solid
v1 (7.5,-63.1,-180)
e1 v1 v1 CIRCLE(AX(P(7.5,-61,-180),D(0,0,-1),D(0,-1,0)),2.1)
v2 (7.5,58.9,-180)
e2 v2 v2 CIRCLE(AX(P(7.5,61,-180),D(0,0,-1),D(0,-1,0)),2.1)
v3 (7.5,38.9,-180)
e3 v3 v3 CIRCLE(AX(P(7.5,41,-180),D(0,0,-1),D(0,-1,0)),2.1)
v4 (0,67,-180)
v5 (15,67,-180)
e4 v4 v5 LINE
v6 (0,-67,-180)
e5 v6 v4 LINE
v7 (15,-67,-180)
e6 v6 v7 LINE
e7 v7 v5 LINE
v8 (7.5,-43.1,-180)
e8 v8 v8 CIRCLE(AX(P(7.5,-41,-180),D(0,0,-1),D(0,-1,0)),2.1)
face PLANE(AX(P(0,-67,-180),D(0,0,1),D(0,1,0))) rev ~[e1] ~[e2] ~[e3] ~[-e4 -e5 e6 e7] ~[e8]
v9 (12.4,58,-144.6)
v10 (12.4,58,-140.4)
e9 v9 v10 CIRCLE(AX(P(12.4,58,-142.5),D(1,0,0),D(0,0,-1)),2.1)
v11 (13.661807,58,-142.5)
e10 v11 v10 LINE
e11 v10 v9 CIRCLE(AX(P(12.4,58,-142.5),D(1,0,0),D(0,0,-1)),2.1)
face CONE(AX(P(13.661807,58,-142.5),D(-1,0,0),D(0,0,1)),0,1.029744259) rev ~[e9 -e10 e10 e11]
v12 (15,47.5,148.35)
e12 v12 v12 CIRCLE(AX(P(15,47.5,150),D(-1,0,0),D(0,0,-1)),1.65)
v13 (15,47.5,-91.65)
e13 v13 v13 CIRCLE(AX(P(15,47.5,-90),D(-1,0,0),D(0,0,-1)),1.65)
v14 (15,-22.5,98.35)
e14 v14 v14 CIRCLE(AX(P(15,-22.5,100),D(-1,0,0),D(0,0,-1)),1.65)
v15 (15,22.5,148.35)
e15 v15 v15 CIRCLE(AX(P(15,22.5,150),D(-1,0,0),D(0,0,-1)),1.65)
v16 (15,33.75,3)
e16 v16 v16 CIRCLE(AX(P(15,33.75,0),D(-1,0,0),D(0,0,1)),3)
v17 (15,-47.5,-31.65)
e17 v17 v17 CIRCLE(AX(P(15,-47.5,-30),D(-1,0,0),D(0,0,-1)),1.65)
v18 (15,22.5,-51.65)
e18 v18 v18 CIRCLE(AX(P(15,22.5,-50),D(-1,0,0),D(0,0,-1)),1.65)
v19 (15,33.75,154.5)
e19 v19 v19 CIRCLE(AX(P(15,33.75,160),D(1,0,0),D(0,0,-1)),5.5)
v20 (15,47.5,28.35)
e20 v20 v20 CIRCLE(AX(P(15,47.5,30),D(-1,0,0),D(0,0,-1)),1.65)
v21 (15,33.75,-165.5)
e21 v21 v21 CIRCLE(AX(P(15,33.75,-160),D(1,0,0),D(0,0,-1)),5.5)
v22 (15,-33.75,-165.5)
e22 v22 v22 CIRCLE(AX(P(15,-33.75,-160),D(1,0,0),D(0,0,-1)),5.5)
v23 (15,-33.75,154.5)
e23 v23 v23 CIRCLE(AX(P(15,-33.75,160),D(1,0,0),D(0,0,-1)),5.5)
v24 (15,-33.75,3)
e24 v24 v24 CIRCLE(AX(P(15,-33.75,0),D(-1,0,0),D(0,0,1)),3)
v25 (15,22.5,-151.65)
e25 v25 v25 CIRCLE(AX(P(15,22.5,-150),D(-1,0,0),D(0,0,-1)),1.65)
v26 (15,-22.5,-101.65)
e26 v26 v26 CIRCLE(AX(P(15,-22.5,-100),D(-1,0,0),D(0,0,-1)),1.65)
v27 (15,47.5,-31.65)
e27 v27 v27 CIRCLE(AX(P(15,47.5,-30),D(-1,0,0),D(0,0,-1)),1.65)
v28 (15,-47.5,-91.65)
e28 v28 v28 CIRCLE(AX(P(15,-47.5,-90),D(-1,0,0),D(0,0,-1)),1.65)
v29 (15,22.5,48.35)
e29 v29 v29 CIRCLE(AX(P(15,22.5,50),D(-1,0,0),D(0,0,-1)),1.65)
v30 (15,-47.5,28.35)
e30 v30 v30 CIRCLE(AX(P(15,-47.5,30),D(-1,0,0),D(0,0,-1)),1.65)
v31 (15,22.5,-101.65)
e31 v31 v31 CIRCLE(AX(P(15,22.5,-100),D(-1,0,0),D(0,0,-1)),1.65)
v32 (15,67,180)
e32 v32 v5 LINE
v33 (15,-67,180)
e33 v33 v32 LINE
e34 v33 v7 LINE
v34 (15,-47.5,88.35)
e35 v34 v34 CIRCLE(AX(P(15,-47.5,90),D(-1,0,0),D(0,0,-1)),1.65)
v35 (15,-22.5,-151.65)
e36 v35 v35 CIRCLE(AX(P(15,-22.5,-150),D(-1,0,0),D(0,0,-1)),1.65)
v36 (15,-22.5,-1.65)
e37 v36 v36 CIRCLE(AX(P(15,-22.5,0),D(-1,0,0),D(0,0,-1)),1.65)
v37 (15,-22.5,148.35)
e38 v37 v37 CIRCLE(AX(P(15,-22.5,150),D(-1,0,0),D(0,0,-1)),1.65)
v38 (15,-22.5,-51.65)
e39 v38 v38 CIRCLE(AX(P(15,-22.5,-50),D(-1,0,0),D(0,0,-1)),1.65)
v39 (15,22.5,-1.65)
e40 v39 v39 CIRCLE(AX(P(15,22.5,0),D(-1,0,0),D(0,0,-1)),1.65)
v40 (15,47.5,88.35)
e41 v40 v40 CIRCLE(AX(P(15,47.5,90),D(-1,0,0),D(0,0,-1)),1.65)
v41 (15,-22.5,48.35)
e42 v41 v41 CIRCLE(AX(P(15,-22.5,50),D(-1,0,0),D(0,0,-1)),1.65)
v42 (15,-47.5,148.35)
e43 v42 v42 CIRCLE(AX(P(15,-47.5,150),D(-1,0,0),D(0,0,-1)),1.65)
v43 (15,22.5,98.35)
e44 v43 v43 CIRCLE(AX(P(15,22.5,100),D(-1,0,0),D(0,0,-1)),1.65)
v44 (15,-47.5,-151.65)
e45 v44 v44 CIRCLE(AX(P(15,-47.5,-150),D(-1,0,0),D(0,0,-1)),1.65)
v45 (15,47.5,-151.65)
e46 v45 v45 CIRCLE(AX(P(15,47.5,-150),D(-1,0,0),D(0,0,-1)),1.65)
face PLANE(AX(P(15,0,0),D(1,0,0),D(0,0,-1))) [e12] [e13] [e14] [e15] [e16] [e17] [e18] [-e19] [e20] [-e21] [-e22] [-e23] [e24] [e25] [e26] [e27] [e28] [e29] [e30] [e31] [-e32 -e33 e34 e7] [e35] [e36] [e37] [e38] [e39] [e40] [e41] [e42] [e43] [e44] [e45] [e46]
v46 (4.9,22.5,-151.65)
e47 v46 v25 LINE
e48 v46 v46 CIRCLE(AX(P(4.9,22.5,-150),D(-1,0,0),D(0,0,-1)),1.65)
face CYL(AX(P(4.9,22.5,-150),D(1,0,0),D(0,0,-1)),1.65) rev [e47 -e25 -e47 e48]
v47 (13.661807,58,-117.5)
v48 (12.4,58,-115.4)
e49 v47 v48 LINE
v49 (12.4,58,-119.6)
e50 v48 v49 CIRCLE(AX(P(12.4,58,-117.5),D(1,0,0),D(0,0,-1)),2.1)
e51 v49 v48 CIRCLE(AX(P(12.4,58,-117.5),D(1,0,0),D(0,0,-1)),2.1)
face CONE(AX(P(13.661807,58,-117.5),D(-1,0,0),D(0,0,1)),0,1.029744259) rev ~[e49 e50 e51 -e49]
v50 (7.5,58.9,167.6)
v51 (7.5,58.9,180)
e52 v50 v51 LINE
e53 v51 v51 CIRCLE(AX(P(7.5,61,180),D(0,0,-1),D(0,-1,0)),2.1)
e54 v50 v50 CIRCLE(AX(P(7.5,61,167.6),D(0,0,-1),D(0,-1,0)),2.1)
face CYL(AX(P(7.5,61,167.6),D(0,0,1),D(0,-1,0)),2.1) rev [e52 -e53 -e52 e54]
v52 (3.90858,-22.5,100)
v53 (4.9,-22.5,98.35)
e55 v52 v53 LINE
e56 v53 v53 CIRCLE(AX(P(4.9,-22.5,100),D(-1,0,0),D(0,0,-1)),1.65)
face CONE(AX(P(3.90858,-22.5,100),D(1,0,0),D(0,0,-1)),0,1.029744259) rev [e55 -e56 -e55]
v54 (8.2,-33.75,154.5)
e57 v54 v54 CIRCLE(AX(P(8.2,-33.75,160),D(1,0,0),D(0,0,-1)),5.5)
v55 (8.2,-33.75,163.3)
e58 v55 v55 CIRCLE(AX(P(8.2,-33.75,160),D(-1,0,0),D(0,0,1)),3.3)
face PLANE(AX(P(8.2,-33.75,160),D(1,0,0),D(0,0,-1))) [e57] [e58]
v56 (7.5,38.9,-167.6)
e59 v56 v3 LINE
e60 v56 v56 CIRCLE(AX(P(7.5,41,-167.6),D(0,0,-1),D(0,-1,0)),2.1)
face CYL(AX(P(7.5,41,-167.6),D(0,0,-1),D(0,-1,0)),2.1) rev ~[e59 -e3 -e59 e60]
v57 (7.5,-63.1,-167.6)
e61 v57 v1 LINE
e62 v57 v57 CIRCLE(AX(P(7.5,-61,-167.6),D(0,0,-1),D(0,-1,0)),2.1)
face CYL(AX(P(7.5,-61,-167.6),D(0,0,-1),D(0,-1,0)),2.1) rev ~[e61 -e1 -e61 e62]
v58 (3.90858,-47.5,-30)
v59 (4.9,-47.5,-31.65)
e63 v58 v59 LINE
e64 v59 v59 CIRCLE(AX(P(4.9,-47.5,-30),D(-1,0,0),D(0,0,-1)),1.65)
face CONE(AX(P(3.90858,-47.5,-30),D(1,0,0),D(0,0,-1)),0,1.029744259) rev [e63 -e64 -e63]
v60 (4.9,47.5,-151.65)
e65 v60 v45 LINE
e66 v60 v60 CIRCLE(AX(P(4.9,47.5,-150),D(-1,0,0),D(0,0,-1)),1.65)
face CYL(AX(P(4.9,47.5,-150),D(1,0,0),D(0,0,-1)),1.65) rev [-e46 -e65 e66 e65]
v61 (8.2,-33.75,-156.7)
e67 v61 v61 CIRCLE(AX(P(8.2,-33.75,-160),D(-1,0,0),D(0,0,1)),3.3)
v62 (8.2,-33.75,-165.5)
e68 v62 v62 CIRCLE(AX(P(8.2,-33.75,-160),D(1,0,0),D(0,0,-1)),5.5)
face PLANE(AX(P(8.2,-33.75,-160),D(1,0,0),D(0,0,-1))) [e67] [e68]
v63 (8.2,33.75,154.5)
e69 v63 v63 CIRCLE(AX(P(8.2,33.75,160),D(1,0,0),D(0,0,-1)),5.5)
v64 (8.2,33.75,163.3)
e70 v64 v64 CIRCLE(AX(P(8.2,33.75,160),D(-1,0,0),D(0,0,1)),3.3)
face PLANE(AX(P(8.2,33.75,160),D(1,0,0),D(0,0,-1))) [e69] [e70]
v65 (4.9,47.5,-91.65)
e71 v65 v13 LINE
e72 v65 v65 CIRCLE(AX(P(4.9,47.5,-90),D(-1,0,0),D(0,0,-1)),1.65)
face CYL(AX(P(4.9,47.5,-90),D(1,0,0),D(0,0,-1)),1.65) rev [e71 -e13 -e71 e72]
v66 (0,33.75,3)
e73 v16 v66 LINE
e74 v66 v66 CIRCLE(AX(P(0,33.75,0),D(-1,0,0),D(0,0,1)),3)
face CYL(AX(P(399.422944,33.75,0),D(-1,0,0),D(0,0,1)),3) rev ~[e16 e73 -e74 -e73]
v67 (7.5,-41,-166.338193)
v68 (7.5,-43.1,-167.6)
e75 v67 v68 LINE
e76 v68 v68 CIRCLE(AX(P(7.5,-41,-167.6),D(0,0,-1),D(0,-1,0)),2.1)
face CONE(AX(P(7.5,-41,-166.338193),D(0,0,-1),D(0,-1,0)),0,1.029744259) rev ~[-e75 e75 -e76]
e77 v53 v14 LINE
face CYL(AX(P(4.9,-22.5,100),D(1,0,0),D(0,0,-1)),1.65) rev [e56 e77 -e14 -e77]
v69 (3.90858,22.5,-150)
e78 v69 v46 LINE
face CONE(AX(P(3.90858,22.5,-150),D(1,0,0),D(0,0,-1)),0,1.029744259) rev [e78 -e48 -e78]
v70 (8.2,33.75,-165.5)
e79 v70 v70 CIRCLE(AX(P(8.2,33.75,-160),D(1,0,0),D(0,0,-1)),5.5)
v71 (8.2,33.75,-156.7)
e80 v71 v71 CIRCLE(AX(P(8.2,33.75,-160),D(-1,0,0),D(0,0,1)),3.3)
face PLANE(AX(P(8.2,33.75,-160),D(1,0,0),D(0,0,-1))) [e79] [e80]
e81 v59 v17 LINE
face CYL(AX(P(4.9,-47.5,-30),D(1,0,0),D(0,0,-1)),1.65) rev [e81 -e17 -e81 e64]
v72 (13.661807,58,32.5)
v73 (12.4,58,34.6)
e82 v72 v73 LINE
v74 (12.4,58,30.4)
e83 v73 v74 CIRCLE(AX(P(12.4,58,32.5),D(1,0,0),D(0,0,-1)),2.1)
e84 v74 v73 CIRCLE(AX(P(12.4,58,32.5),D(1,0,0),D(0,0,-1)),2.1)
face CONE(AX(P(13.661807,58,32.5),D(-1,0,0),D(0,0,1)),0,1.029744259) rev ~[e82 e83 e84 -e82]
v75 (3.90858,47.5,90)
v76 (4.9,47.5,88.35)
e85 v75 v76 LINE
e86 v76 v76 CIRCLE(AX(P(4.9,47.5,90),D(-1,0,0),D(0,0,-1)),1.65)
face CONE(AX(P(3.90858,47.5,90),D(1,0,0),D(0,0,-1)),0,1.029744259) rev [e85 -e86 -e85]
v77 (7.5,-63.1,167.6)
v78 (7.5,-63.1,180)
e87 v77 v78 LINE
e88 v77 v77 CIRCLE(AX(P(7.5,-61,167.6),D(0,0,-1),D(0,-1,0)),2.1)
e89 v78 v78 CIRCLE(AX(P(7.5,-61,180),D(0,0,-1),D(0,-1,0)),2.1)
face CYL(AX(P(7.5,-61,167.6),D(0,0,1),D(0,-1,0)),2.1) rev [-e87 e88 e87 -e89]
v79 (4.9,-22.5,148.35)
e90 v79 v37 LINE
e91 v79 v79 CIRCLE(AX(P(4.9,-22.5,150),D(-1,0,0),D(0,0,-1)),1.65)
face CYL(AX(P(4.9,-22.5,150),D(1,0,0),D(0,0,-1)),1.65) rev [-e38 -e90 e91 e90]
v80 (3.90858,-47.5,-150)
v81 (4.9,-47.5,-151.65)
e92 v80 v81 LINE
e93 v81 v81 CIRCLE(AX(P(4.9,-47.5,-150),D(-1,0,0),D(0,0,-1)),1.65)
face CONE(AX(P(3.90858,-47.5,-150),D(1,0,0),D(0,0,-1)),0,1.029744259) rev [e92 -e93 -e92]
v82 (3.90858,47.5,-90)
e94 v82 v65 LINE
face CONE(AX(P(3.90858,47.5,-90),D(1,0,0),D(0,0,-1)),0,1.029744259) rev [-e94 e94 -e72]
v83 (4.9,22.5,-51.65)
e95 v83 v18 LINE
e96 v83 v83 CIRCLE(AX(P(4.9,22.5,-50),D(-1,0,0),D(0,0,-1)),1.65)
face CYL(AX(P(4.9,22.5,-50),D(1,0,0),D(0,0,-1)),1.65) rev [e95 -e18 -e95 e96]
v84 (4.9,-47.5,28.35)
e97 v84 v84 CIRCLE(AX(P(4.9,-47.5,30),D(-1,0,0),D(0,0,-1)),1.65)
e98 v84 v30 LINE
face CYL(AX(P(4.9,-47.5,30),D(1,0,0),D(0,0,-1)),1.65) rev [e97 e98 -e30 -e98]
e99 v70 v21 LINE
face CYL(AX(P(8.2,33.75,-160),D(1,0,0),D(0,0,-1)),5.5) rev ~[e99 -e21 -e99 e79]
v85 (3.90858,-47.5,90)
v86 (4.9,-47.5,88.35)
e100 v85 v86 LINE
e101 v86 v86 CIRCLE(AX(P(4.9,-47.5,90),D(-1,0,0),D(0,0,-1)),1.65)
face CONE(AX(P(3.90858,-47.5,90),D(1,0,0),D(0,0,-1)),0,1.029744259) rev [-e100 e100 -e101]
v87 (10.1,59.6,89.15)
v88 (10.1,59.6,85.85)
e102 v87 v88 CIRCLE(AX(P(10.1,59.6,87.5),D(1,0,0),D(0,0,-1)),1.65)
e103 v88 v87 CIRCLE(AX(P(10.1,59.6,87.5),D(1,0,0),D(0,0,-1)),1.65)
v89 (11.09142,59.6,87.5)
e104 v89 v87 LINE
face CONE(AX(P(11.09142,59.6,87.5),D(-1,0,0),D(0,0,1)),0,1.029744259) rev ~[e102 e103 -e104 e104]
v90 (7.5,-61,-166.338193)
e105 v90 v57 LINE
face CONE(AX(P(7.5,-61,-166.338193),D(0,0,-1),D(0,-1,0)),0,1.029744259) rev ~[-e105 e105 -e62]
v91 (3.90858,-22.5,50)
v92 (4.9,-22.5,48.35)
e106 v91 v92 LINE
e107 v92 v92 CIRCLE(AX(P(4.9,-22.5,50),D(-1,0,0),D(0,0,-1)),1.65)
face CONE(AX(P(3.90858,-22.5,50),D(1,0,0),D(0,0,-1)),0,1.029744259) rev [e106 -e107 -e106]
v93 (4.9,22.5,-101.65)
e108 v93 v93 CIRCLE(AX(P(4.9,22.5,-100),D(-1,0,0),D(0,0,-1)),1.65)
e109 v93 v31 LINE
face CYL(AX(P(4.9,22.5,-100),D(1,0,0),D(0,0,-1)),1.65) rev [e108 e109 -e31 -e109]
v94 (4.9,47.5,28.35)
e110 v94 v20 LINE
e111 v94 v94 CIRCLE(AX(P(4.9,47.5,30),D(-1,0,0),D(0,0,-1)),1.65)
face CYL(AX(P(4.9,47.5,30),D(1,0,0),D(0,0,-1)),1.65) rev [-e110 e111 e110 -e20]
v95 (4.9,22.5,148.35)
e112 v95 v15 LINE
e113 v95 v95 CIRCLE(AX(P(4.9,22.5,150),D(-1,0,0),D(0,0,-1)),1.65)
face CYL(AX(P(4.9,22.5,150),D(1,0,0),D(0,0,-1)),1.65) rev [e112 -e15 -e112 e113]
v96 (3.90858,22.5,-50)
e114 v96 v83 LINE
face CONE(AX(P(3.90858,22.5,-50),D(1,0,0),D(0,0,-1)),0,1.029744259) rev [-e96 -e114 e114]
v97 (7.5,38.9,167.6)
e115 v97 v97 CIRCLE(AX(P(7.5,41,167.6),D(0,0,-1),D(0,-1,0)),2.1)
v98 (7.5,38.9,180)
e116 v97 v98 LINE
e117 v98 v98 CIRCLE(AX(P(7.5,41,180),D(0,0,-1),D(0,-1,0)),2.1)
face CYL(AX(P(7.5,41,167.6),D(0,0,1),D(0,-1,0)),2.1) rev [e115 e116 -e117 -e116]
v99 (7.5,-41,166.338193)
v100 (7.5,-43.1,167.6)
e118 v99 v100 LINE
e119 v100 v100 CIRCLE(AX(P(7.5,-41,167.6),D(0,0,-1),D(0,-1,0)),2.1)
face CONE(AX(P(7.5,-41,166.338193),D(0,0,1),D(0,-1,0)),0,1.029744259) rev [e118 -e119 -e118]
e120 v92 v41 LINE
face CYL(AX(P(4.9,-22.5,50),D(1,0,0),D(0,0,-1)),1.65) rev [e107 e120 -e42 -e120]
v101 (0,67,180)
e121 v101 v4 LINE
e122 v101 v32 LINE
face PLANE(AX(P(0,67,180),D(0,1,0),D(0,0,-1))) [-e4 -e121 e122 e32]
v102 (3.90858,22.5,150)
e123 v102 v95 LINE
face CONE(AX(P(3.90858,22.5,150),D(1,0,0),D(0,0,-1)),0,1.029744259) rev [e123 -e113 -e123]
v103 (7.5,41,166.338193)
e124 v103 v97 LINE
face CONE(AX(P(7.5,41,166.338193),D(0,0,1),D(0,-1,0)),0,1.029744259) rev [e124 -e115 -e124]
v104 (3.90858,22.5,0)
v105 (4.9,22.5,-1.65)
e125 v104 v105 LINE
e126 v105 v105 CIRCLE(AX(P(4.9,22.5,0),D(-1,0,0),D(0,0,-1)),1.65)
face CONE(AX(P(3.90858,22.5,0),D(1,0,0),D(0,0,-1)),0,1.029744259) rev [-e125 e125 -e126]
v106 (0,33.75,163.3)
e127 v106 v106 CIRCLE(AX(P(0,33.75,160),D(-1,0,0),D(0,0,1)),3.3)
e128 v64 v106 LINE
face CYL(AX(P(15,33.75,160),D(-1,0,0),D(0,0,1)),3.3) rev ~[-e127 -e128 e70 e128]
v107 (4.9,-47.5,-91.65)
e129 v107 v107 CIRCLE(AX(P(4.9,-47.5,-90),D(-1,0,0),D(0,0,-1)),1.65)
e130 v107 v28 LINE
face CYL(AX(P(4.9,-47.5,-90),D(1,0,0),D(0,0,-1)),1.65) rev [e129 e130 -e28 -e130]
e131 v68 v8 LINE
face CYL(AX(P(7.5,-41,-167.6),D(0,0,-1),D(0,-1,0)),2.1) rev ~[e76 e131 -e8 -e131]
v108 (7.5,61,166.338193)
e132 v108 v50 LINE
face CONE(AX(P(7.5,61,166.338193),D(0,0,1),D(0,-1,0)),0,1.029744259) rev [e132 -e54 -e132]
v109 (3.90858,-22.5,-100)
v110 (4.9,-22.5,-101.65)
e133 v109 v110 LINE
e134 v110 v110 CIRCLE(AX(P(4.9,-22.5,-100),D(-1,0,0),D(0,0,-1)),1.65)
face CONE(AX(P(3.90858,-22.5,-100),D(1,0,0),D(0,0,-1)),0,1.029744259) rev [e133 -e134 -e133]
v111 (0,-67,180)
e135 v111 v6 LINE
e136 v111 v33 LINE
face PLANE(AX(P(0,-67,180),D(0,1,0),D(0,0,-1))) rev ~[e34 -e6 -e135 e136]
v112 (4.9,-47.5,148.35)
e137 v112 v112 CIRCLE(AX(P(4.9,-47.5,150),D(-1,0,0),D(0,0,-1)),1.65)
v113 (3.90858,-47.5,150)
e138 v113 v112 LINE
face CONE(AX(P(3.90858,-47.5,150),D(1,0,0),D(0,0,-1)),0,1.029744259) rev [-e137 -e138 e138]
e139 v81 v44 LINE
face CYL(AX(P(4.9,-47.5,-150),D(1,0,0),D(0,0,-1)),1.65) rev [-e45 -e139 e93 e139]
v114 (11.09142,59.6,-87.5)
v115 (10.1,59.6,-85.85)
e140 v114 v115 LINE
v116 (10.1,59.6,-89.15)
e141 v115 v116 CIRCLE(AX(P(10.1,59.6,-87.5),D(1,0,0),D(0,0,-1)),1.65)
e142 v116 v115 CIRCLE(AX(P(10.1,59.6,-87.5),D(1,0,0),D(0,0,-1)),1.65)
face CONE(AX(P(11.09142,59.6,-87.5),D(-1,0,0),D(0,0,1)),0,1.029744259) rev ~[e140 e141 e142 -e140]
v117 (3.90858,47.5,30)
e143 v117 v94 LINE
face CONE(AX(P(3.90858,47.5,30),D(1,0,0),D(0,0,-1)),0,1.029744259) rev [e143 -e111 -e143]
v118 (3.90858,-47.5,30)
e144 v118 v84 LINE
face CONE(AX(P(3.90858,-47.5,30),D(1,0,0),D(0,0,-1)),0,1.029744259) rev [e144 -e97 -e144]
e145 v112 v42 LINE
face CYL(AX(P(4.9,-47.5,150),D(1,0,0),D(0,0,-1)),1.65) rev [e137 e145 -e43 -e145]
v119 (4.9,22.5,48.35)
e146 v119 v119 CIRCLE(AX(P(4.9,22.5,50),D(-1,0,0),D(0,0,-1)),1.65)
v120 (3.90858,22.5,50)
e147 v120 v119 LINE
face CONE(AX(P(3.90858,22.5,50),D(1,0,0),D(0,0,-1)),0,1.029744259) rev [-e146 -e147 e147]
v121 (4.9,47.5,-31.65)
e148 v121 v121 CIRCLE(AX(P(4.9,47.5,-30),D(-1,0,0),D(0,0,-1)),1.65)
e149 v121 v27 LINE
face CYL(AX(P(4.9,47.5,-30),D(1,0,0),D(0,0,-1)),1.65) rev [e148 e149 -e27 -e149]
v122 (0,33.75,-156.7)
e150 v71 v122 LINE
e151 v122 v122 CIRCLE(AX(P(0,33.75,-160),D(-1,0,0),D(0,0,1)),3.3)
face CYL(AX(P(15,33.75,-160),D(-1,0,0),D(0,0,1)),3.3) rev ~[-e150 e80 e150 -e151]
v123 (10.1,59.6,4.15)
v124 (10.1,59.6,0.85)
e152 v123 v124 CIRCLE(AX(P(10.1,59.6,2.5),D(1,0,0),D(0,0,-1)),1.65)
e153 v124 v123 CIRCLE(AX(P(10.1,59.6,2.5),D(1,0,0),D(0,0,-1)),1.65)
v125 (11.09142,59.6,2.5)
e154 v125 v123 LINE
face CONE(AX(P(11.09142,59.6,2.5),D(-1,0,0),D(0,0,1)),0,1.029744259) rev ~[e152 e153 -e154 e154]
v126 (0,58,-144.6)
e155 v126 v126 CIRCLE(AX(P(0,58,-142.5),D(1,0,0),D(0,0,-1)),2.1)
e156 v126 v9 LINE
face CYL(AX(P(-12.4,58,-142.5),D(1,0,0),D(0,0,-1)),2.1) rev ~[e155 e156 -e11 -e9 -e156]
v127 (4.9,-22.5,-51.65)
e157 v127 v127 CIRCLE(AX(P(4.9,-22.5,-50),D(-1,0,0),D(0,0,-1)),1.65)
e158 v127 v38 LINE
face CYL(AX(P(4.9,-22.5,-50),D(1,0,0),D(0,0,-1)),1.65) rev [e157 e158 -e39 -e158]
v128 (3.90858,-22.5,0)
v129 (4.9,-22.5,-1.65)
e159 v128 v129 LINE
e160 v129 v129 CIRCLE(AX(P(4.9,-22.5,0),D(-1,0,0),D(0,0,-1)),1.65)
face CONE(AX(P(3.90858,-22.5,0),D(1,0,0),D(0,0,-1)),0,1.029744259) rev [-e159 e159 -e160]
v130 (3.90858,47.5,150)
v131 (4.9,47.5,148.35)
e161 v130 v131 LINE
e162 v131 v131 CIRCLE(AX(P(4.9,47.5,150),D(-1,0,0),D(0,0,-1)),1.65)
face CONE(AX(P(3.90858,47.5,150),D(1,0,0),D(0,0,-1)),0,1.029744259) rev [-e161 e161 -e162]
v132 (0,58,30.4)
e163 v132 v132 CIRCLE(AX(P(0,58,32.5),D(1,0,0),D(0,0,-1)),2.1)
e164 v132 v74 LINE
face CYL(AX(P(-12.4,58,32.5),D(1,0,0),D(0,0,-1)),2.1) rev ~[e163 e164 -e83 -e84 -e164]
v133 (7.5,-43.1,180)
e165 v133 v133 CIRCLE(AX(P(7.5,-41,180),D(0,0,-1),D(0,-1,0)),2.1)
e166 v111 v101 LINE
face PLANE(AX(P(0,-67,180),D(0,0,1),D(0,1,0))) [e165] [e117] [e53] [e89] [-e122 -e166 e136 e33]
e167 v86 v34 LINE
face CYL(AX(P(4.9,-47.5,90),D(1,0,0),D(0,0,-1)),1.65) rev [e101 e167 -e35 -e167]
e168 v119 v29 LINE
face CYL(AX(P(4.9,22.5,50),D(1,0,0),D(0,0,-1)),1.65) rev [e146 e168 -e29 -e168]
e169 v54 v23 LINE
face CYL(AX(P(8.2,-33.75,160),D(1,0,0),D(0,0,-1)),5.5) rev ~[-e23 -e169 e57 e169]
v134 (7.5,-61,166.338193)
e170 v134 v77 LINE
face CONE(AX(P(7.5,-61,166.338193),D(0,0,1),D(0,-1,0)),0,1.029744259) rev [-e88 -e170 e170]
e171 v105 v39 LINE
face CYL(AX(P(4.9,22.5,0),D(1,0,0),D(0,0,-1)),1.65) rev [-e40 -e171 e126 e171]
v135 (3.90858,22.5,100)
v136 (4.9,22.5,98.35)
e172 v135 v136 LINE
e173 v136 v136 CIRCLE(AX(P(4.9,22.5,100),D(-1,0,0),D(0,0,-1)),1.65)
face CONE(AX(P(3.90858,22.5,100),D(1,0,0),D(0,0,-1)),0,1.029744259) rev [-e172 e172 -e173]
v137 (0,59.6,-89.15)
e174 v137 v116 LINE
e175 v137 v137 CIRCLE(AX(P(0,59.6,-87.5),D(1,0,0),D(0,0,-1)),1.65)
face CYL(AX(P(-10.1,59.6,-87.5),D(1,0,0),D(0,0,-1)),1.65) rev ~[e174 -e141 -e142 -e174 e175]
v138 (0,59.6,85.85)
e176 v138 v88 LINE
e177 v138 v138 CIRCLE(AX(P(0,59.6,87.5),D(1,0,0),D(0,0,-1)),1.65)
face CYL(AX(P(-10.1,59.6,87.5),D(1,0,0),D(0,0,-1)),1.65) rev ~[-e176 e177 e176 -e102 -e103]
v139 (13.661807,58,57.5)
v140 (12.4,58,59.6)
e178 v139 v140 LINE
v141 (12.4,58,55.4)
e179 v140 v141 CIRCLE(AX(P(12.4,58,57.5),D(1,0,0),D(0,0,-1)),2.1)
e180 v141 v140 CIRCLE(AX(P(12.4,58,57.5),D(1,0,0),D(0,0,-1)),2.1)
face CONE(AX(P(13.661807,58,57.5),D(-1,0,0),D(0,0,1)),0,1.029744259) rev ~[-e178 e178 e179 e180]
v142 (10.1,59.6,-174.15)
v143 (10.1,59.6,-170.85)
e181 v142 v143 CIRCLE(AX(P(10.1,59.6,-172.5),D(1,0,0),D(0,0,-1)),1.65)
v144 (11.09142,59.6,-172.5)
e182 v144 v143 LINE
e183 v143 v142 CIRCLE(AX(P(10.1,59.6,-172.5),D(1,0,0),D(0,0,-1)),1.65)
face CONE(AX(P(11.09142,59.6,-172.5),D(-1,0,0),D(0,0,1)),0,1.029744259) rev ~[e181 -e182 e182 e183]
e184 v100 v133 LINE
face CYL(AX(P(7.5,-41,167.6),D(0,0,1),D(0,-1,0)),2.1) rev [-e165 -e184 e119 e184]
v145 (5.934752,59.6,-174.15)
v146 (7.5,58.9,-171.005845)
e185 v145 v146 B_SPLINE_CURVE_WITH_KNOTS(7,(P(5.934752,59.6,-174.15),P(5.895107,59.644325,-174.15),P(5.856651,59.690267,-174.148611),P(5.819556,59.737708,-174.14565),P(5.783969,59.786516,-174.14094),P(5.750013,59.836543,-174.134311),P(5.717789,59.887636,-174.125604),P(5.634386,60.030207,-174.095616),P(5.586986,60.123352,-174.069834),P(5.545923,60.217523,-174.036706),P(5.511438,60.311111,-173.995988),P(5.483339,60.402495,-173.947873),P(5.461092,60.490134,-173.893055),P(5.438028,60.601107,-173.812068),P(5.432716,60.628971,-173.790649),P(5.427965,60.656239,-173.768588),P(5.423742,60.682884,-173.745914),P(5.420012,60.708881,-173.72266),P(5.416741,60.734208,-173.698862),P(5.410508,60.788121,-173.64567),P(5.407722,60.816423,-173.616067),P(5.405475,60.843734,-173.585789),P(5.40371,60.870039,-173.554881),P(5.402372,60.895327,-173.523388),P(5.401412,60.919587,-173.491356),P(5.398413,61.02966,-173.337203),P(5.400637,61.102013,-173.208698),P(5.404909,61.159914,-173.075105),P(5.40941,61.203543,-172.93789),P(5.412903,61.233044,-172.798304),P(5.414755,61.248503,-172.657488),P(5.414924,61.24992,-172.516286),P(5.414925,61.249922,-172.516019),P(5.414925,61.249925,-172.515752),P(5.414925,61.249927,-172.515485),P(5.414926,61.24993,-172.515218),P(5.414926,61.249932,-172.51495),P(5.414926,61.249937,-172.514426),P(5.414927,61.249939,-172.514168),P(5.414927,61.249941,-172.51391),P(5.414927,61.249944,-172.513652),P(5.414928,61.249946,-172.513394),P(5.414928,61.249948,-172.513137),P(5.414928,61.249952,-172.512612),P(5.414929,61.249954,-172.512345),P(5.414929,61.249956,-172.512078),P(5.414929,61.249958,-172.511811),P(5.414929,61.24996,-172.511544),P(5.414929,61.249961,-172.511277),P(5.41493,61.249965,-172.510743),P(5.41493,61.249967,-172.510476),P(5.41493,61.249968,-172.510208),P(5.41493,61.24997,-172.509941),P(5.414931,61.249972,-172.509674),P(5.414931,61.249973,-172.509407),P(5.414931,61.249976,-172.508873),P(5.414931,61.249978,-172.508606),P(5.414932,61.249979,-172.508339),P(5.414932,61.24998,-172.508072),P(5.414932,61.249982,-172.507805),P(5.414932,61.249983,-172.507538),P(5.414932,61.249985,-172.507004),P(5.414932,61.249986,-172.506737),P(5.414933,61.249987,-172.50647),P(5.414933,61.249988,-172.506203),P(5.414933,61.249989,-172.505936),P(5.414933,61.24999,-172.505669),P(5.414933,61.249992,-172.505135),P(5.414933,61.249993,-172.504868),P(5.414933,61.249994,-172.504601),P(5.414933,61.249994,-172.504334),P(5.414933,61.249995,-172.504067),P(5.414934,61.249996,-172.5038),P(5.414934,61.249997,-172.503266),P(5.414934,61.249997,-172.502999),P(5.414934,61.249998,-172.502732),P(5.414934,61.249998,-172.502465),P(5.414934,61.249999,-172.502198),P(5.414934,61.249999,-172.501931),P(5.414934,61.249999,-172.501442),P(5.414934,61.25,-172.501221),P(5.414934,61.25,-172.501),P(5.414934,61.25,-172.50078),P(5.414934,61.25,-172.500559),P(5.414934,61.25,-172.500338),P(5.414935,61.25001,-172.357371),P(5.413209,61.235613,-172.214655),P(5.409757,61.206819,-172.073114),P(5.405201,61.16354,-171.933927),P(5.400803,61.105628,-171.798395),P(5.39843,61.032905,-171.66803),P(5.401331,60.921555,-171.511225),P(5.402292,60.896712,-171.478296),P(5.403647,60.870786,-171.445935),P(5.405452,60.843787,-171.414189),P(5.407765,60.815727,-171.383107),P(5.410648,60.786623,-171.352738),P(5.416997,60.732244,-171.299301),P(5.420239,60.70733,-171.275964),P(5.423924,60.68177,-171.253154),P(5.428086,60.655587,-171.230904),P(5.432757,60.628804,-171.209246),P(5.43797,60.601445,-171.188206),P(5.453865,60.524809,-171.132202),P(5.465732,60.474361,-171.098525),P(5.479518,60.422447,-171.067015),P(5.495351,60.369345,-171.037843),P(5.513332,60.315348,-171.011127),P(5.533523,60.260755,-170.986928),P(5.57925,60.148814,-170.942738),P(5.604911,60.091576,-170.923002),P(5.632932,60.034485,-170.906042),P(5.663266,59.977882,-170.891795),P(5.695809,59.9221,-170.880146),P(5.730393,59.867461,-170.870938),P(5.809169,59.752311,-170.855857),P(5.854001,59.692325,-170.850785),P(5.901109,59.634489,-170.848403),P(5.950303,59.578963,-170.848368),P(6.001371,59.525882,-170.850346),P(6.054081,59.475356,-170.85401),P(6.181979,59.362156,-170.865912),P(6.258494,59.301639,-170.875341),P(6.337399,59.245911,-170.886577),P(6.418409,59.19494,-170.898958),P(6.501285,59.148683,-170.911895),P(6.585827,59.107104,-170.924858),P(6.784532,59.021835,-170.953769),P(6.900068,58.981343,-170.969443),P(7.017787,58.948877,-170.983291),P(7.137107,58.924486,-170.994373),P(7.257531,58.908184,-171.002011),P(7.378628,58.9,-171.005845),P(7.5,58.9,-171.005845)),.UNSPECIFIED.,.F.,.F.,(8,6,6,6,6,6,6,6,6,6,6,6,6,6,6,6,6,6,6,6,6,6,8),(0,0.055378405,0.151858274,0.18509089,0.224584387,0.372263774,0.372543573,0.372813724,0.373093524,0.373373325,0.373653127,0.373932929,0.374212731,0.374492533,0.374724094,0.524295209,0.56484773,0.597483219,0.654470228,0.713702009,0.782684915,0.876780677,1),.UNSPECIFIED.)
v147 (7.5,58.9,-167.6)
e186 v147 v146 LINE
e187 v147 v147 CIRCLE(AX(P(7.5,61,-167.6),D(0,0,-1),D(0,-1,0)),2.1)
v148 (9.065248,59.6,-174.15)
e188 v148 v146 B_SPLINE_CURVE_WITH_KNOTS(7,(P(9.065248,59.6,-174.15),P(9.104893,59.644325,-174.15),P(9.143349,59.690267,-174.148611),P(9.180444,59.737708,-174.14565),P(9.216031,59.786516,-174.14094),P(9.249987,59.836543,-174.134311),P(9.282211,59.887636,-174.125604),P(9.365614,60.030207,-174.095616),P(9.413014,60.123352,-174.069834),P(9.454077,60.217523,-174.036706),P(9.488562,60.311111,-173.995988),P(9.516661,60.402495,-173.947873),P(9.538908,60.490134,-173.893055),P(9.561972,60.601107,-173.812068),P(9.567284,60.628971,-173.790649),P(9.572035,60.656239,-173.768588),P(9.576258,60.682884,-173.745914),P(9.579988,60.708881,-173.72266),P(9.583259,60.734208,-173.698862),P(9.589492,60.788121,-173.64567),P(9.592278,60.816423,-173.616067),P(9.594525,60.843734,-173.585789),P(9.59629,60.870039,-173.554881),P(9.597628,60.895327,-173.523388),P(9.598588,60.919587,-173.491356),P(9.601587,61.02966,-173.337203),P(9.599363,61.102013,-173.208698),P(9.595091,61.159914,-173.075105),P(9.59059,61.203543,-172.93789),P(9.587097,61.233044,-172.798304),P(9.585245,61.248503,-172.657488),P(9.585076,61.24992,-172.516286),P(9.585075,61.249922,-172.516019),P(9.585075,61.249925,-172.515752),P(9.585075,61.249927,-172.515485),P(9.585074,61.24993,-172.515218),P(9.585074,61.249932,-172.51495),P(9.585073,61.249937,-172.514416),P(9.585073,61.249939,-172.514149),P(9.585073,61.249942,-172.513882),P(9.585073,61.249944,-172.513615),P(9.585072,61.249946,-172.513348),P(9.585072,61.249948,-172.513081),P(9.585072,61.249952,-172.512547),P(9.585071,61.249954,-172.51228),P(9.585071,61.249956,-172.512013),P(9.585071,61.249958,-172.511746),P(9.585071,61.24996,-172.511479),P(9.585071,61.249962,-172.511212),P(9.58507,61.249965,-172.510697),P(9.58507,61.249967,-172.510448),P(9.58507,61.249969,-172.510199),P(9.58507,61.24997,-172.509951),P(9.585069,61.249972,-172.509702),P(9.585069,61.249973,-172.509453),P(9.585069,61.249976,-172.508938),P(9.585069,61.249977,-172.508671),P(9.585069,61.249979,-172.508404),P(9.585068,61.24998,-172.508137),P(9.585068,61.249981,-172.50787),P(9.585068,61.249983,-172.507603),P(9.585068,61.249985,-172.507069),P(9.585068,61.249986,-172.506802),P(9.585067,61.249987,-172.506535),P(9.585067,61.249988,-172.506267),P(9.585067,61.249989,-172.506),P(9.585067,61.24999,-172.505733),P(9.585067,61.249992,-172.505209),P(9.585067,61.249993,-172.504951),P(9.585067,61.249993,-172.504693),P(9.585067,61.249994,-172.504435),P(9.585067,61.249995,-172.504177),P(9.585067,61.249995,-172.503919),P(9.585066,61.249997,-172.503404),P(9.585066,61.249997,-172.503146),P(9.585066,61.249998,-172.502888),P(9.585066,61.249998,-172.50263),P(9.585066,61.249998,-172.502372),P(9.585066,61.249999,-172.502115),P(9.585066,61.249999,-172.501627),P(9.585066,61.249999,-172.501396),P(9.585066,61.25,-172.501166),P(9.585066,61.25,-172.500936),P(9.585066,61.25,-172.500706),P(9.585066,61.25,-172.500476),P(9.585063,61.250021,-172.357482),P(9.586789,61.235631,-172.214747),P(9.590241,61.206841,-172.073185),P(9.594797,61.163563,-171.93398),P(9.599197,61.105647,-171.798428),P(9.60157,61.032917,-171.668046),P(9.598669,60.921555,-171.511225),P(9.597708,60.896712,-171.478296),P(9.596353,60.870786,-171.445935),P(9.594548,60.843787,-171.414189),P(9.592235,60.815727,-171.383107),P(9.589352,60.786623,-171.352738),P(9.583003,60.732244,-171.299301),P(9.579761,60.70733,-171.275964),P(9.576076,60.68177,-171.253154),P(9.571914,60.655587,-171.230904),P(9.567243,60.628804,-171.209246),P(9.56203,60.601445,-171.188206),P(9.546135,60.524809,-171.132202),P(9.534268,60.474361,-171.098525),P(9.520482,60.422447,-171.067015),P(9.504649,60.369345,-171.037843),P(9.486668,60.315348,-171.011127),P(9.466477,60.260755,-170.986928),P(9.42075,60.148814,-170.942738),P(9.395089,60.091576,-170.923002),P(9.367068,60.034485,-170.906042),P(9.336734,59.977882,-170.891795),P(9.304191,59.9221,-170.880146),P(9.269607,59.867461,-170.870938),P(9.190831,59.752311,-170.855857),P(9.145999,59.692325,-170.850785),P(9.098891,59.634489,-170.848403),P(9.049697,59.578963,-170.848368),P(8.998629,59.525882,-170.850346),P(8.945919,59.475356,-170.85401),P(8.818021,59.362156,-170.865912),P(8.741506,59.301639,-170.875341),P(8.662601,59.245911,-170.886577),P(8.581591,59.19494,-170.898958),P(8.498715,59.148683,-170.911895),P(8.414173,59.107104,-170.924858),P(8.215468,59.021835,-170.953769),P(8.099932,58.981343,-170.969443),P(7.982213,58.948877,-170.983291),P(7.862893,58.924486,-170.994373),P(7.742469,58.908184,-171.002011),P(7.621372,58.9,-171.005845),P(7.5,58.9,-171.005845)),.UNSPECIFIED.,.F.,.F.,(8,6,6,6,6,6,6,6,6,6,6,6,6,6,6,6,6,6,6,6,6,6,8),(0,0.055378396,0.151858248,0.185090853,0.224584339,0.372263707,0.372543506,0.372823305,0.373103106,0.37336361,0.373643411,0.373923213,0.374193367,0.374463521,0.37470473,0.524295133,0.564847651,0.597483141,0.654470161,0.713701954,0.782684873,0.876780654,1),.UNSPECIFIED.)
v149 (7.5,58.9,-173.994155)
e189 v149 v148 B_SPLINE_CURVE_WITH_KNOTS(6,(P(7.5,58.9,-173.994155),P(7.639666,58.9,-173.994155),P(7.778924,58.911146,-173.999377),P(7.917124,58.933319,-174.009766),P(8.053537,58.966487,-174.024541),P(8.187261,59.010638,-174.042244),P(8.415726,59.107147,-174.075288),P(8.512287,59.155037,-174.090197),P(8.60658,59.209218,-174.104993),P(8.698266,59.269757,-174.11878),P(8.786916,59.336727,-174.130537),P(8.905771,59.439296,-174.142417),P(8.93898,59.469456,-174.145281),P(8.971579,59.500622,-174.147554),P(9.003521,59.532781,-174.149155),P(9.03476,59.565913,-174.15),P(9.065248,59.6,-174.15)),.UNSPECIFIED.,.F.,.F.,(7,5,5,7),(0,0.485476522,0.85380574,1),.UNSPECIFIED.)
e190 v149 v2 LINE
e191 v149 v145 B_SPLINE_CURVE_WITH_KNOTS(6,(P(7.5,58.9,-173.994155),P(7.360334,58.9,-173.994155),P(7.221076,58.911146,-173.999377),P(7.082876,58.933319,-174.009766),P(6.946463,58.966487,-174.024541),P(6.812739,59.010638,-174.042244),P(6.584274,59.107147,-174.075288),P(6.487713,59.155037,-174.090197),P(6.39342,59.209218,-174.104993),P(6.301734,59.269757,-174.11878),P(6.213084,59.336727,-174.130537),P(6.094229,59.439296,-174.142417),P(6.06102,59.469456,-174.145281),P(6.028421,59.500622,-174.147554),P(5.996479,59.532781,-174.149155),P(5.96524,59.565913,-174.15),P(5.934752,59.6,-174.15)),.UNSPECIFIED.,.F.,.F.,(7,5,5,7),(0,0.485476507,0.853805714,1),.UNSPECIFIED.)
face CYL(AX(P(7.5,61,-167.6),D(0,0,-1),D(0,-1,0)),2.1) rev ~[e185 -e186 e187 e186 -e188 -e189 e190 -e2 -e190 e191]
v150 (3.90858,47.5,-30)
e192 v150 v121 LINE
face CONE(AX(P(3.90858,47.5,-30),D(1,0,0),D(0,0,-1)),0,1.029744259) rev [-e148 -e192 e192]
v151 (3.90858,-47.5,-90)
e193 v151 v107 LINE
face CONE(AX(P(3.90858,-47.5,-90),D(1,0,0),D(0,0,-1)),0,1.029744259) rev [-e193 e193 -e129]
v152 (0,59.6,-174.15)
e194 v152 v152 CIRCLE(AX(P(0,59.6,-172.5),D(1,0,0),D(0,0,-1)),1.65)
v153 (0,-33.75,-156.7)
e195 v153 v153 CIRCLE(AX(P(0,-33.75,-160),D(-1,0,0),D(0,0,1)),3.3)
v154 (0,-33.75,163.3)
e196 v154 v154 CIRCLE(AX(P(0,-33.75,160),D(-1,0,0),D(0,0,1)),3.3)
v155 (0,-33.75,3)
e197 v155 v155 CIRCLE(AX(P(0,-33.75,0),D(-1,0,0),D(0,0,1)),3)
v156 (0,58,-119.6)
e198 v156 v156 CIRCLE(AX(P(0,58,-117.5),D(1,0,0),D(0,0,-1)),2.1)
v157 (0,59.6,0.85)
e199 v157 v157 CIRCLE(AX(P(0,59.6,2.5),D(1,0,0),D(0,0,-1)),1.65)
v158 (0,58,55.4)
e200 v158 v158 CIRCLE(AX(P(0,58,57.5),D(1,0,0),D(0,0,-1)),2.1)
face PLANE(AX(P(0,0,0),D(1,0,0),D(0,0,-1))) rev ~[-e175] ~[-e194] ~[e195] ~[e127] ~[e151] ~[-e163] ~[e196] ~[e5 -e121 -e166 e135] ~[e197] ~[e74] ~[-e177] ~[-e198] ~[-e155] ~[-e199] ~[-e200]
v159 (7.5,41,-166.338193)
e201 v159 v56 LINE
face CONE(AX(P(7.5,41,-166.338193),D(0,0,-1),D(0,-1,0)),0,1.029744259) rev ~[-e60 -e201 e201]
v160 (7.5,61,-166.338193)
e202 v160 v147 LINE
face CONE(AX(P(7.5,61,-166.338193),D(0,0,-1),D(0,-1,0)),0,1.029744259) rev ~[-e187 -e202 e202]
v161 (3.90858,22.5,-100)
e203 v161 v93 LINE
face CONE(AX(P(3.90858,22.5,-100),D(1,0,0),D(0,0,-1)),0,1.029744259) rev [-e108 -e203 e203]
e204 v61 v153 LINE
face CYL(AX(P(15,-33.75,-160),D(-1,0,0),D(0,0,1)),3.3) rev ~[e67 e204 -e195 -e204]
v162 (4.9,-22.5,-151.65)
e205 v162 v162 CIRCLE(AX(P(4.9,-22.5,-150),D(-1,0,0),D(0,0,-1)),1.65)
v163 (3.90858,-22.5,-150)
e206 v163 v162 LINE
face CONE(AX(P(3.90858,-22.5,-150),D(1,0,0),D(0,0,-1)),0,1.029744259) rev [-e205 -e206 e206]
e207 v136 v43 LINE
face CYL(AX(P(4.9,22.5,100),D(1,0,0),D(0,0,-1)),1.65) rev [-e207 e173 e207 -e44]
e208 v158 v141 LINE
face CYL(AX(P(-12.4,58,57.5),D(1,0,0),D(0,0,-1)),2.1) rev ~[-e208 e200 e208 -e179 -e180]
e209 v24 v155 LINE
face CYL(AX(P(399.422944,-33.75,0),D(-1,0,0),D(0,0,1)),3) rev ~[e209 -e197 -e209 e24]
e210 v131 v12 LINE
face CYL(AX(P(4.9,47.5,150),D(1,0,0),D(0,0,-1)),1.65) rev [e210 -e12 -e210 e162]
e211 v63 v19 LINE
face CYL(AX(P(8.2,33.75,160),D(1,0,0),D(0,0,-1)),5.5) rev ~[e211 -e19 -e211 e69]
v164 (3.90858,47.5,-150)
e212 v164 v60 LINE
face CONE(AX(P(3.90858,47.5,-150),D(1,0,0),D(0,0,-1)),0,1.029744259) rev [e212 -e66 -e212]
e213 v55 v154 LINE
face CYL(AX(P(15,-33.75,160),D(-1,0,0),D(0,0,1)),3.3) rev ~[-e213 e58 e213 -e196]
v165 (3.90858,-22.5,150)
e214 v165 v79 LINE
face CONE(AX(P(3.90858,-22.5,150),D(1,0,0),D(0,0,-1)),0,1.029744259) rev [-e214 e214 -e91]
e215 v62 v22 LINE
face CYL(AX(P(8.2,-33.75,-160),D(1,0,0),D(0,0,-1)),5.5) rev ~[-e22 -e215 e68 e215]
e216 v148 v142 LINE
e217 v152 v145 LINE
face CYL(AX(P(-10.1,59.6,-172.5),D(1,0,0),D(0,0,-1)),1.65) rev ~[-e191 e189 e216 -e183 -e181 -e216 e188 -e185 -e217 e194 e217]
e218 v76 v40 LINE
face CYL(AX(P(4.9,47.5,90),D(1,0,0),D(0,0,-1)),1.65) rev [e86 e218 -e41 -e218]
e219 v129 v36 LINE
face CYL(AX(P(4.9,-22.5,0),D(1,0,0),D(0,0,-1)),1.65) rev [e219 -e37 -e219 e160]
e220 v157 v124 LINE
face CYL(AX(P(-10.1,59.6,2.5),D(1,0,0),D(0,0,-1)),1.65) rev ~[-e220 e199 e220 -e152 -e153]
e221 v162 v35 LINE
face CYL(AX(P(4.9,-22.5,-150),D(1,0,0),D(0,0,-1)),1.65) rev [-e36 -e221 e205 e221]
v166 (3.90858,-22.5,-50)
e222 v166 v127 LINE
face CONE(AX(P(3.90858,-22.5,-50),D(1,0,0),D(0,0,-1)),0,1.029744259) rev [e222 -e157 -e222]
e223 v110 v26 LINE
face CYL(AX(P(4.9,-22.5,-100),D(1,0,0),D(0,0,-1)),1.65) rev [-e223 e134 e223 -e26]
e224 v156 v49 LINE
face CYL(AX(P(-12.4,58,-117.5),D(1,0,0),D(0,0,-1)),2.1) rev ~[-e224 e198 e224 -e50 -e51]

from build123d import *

# Parameters (mm, degrees)
SKETCH1_W                                            = 360
SKETCH1_H                                            = 134
BOSS_EXTRUDE1_DEPTH                                  = 15
M5_TAPPED_HOLE1_AT_2_COUNT                           = 2
M5_TAPPED_HOLE1_AT_2_PITCH                           = 122
M5_TAPPED_HOLE1_AT_3_COUNT                           = 2
M5_TAPPED_HOLE1_AT_3_PITCH                           = 102
M5_TAPPED_HOLE1_AT_4_COUNT                           = 2
M5_TAPPED_HOLE1_AT_4_PITCH                           = 20
M4_TAPPED_HOLE1_AT_2_COUNT                           = 2
M4_TAPPED_HOLE1_AT_2_PITCH                           = 45
LPATTERN1_COUNT                                      = 7
LPATTERN1_PITCH                                      = 50
M4_TAPPED_HOLE2_AT_2_COUNT                           = 2
M4_TAPPED_HOLE2_AT_2_PITCH                           = 95
LPATTERN2_COUNT                                      = 6
LPATTERN2_PITCH                                      = 60
M5_TAPPED_HOLE2_D                                    = 4.2
M5_TAPPED_HOLE2_DEPTH                                = 12.4
M5_TAPPED_HOLE2_TIP                                  = 1.2618073
M4_TAPPED_HOLE3_D                                    = 3.3
M4_TAPPED_HOLE3_DEPTH                                = 10.1
M4_TAPPED_HOLE3_TIP                                  = 0.991420021
CBORE_FOR_M6_HEXAGON_SOCKET_HEAD_CAP_SCR_D           = 6.6
CBORE_FOR_M6_HEXAGON_SOCKET_HEAD_CAP_SCR_CBORE_D     = 11
CBORE_FOR_M6_HEXAGON_SOCKET_HEAD_CAP_SCR_CBORE_DEPTH = 6.8
F_6_0MM_DOWEL_HOLE1_D                                = 6


with BuildPart() as part:
    # Sketch1 → Boss-Extrude1 (new body)
    with BuildSketch(Plane(origin=(0, 0, 0), x_dir=(0, 0, -1), z_dir=(1, 0, 0))):
        Rectangle(SKETCH1_W, SKETCH1_H)
    extrude(amount=BOSS_EXTRUDE1_DEPTH)

    # Sketch3 → M5 Tapped Hole1 (revolve, cut)
    with BuildSketch(Plane(origin=(7.5, -61, 180), x_dir=(0, -1, 0), z_dir=(1, 0, 0))):
        Polygon((0, 0), (0, 13.6618073), (2.1, 12.4), (2.1, 0), align=None)
    m5_tapped_hole1 = revolve(axis=Axis((7.5, -61, 186.35), (0, 0, -1)), mode=Mode.SUBTRACT)

    # M5 Tapped Hole1 at 2: M5 Tapped Hole1 ×2
    with Locations(*[(0, i * M5_TAPPED_HOLE1_AT_2_PITCH, 0) for i in range(1, M5_TAPPED_HOLE1_AT_2_COUNT)]):
        add(m5_tapped_hole1, mode=Mode.SUBTRACT)

    # M5 Tapped Hole1 at 3: M5 Tapped Hole1 ×2
    with Locations(*[(0, i * M5_TAPPED_HOLE1_AT_3_PITCH, 0) for i in range(1, M5_TAPPED_HOLE1_AT_3_COUNT)]):
        add(m5_tapped_hole1, mode=Mode.SUBTRACT)

    # M5 Tapped Hole1 at 4: M5 Tapped Hole1 ×2
    with Locations(*[(0, i * M5_TAPPED_HOLE1_AT_4_PITCH, 0) for i in range(1, M5_TAPPED_HOLE1_AT_4_COUNT)]):
        add(m5_tapped_hole1, mode=Mode.SUBTRACT)

    # Mirror1: M5 Tapped Hole1 across plane
    add(m5_tapped_hole1.mirror(Plane.XY), mode=Mode.SUBTRACT)

    # Mirror1 copy 1 sketch → Mirror1 copy 1 (revolve, cut)
    with BuildSketch(Plane(origin=(7.5, 61, -180), x_dir=(0, -1, 0), z_dir=(1, 0, 0))):
        Polygon((0, 0), (0, -13.6618073), (2.1, -12.4), (2.1, 0), align=None)
    revolve(axis=Axis((7.5, 61, -186.35), (0, 0, -1)), mode=Mode.SUBTRACT)

    # Mirror1 copy 2 sketch → Mirror1 copy 2 (revolve, cut)
    with BuildSketch(Plane(origin=(7.5, 41, -180), x_dir=(0, -1, 0), z_dir=(1, 0, 0))):
        Polygon((0, 0), (0, -13.6618073), (2.1, -12.4), (2.1, 0), align=None)
    revolve(axis=Axis((7.5, 41, -186.35), (0, 0, -1)), mode=Mode.SUBTRACT)

    # Mirror1 copy 3 sketch → Mirror1 copy 3 (revolve, cut)
    with BuildSketch(Plane(origin=(7.5, -41, -180), x_dir=(0, -1, 0), z_dir=(1, 0, 0))):
        Polygon((0, 0), (0, -13.6618073), (2.1, -12.4), (2.1, 0), align=None)
    revolve(axis=Axis((7.5, -41, -186.35), (0, 0, -1)), mode=Mode.SUBTRACT)

    # Sketch5 → M4 Tapped Hole1 (revolve, cut)
    with BuildSketch(Plane(origin=(15, 22.5, -150), x_dir=(0, 0, -1), z_dir=(0, 1, 0))):
        Polygon((0, 0), (0, 11.091420021), (1.65, 10.1), (1.65, 0), align=None)
    m4_tapped_hole1 = revolve(axis=Axis((21.35, 22.5, -150), (-1, 0, 0)), mode=Mode.SUBTRACT)

    # M4 Tapped Hole1 at 2: M4 Tapped Hole1 ×2
    with Locations(*[(0, -i * M4_TAPPED_HOLE1_AT_2_PITCH, 0) for i in range(1, M4_TAPPED_HOLE1_AT_2_COUNT)]):
        add(m4_tapped_hole1, mode=Mode.SUBTRACT)

    # LPattern1: M4 Tapped Hole1 ×7
    with Locations(*[(0, 0, i * LPATTERN1_PITCH) for i in range(1, LPATTERN1_COUNT)]):
        add(m4_tapped_hole1, mode=Mode.SUBTRACT)

    # LPattern1 copy 1 sketch → LPattern1 copy 1 (revolve, cut)
    with BuildSketch(Plane(origin=(15, -22.5, -100), x_dir=(0, 0, -1), z_dir=(0, 1, 0))):
        Polygon((0, 0), (0, 11.091420021), (1.65, 10.1), (1.65, 0), align=None)
    revolve(axis=Axis((21.35, -22.5, -100), (-1, 0, 0)), mode=Mode.SUBTRACT)

    # LPattern1 copy 2 sketch → LPattern1 copy 2 (revolve, cut)
    with BuildSketch(Plane(origin=(15, -22.5, -50), x_dir=(0, 0, -1), z_dir=(0, 1, 0))):
        Polygon((0, 0), (0, 11.091420021), (1.65, 10.1), (1.65, 0), align=None)
    revolve(axis=Axis((21.35, -22.5, -50), (-1, 0, 0)), mode=Mode.SUBTRACT)

    # LPattern1 copy 3 sketch → LPattern1 copy 3 (revolve, cut)
    with BuildSketch(Plane(origin=(15, -22.5, 0), x_dir=(0, 0, -1), z_dir=(0, 1, 0))):
        Polygon((0, 0), (0, 11.091420021), (1.65, 10.1), (1.65, 0), align=None)
    revolve(axis=Axis((21.35, -22.5, 0), (-1, 0, 0)), mode=Mode.SUBTRACT)

    # LPattern1 copy 4 sketch → LPattern1 copy 4 (revolve, cut)
    with BuildSketch(Plane(origin=(15, -22.5, 50), x_dir=(0, 0, -1), z_dir=(0, 1, 0))):
        Polygon((0, 0), (0, 11.091420021), (1.65, 10.1), (1.65, 0), align=None)
    revolve(axis=Axis((21.35, -22.5, 50), (-1, 0, 0)), mode=Mode.SUBTRACT)

    # LPattern1 copy 5 sketch → LPattern1 copy 5 (revolve, cut)
    with BuildSketch(Plane(origin=(15, -22.5, 100), x_dir=(0, 0, -1), z_dir=(0, 1, 0))):
        Polygon((0, 0), (0, 11.091420021), (1.65, 10.1), (1.65, 0), align=None)
    revolve(axis=Axis((21.35, -22.5, 100), (-1, 0, 0)), mode=Mode.SUBTRACT)

    # LPattern1 copy 6 sketch → LPattern1 copy 6 (revolve, cut)
    with BuildSketch(Plane(origin=(15, -22.5, 150), x_dir=(0, 0, -1), z_dir=(0, 1, 0))):
        Polygon((0, 0), (0, 11.091420021), (1.65, 10.1), (1.65, 0), align=None)
    revolve(axis=Axis((21.35, -22.5, 150), (-1, 0, 0)), mode=Mode.SUBTRACT)

    # Sketch7 → M4 Tapped Hole2 (revolve, cut)
    with BuildSketch(Plane(origin=(15, 47.5, -150), x_dir=(0, 0, -1), z_dir=(0, 1, 0))):
        Polygon((0, 0), (0, 11.091420021), (1.65, 10.1), (1.65, 0), align=None)
    m4_tapped_hole2 = revolve(axis=Axis((21.35, 47.5, -150), (-1, 0, 0)), mode=Mode.SUBTRACT)

    # M4 Tapped Hole2 at 2: M4 Tapped Hole2 ×2
    with Locations(*[(0, -i * M4_TAPPED_HOLE2_AT_2_PITCH, 0) for i in range(1, M4_TAPPED_HOLE2_AT_2_COUNT)]):
        add(m4_tapped_hole2, mode=Mode.SUBTRACT)

    # LPattern2: M4 Tapped Hole2 ×6
    with Locations(*[(0, 0, i * LPATTERN2_PITCH) for i in range(1, LPATTERN2_COUNT)]):
        add(m4_tapped_hole2, mode=Mode.SUBTRACT)

    # LPattern2 copy 1 sketch → LPattern2 copy 1 (revolve, cut)
    with BuildSketch(Plane(origin=(15, -47.5, -90), x_dir=(0, 0, -1), z_dir=(0, 1, 0))):
        Polygon((0, 0), (0, 11.091420021), (1.65, 10.1), (1.65, 0), align=None)
    revolve(axis=Axis((21.35, -47.5, -90), (-1, 0, 0)), mode=Mode.SUBTRACT)

    # LPattern2 copy 2 sketch → LPattern2 copy 2 (revolve, cut)
    with BuildSketch(Plane(origin=(15, -47.5, -30), x_dir=(0, 0, -1), z_dir=(0, 1, 0))):
        Polygon((0, 0), (0, 11.091420021), (1.65, 10.1), (1.65, 0), align=None)
    revolve(axis=Axis((21.35, -47.5, -30), (-1, 0, 0)), mode=Mode.SUBTRACT)

    # LPattern2 copy 3 sketch → LPattern2 copy 3 (revolve, cut)
    with BuildSketch(Plane(origin=(15, -47.5, 30), x_dir=(0, 0, -1), z_dir=(0, 1, 0))):
        Polygon((0, 0), (0, 11.091420021), (1.65, 10.1), (1.65, 0), align=None)
    revolve(axis=Axis((21.35, -47.5, 30), (-1, 0, 0)), mode=Mode.SUBTRACT)

    # LPattern2 copy 4 sketch → LPattern2 copy 4 (revolve, cut)
    with BuildSketch(Plane(origin=(15, -47.5, 90), x_dir=(0, 0, -1), z_dir=(0, 1, 0))):
        Polygon((0, 0), (0, 11.091420021), (1.65, 10.1), (1.65, 0), align=None)
    revolve(axis=Axis((21.35, -47.5, 90), (-1, 0, 0)), mode=Mode.SUBTRACT)

    # LPattern2 copy 5 sketch → LPattern2 copy 5 (revolve, cut)
    with BuildSketch(Plane(origin=(15, -47.5, 150), x_dir=(0, 0, -1), z_dir=(0, 1, 0))):
        Polygon((0, 0), (0, 11.091420021), (1.65, 10.1), (1.65, 0), align=None)
    revolve(axis=Axis((21.35, -47.5, 150), (-1, 0, 0)), mode=Mode.SUBTRACT)

    # M5 Tapped Hole2
    with Locations(Plane.ZY):
        with Locations((-142.5, 58), (-117.5, 58), (32.5, 58), (57.5, 58)):
            Hole(M5_TAPPED_HOLE2_D / 2, depth=M5_TAPPED_HOLE2_DEPTH)
            with Locations((0, 0, -(M5_TAPPED_HOLE2_DEPTH + M5_TAPPED_HOLE2_TIP / 2))):  # 118° drill point
                Cone(0, M5_TAPPED_HOLE2_D / 2, M5_TAPPED_HOLE2_TIP, mode=Mode.SUBTRACT)

    # M4 Tapped Hole3
    with Locations(Plane.ZY):
        with Locations((-172.5, 59.6), (87.5, 59.6), (2.5, 59.6), (-87.5, 59.6)):
            Hole(M4_TAPPED_HOLE3_D / 2, depth=M4_TAPPED_HOLE3_DEPTH)
            with Locations((0, 0, -(M4_TAPPED_HOLE3_DEPTH + M4_TAPPED_HOLE3_TIP / 2))):  # 118° drill point
                Cone(0, M4_TAPPED_HOLE3_D / 2, M4_TAPPED_HOLE3_TIP, mode=Mode.SUBTRACT)

    # CBORE for M6 Hexagon socket head cap screws1 (through all)
    with Locations(Plane(origin=(15, 0, 0), x_dir=(0, 0, -1), z_dir=(1, 0, 0))):
        with Locations((-160, 33.75), (-160, -33.75), (160, -33.75), (160, 33.75)):
            CounterBoreHole(CBORE_FOR_M6_HEXAGON_SOCKET_HEAD_CAP_SCR_D / 2, CBORE_FOR_M6_HEXAGON_SOCKET_HEAD_CAP_SCR_CBORE_D / 2, CBORE_FOR_M6_HEXAGON_SOCKET_HEAD_CAP_SCR_CBORE_DEPTH)

    # Ø6.0mm dowel hole1 (through all)
    with Locations(Plane(origin=(15, 0, 0), x_dir=(0, 0, -1), z_dir=(1, 0, 0))):
        with Locations((0, -33.75), (0, 33.75)):
            Hole(F_6_0MM_DOWEL_HOLE1_D / 2)


solid = part.part
